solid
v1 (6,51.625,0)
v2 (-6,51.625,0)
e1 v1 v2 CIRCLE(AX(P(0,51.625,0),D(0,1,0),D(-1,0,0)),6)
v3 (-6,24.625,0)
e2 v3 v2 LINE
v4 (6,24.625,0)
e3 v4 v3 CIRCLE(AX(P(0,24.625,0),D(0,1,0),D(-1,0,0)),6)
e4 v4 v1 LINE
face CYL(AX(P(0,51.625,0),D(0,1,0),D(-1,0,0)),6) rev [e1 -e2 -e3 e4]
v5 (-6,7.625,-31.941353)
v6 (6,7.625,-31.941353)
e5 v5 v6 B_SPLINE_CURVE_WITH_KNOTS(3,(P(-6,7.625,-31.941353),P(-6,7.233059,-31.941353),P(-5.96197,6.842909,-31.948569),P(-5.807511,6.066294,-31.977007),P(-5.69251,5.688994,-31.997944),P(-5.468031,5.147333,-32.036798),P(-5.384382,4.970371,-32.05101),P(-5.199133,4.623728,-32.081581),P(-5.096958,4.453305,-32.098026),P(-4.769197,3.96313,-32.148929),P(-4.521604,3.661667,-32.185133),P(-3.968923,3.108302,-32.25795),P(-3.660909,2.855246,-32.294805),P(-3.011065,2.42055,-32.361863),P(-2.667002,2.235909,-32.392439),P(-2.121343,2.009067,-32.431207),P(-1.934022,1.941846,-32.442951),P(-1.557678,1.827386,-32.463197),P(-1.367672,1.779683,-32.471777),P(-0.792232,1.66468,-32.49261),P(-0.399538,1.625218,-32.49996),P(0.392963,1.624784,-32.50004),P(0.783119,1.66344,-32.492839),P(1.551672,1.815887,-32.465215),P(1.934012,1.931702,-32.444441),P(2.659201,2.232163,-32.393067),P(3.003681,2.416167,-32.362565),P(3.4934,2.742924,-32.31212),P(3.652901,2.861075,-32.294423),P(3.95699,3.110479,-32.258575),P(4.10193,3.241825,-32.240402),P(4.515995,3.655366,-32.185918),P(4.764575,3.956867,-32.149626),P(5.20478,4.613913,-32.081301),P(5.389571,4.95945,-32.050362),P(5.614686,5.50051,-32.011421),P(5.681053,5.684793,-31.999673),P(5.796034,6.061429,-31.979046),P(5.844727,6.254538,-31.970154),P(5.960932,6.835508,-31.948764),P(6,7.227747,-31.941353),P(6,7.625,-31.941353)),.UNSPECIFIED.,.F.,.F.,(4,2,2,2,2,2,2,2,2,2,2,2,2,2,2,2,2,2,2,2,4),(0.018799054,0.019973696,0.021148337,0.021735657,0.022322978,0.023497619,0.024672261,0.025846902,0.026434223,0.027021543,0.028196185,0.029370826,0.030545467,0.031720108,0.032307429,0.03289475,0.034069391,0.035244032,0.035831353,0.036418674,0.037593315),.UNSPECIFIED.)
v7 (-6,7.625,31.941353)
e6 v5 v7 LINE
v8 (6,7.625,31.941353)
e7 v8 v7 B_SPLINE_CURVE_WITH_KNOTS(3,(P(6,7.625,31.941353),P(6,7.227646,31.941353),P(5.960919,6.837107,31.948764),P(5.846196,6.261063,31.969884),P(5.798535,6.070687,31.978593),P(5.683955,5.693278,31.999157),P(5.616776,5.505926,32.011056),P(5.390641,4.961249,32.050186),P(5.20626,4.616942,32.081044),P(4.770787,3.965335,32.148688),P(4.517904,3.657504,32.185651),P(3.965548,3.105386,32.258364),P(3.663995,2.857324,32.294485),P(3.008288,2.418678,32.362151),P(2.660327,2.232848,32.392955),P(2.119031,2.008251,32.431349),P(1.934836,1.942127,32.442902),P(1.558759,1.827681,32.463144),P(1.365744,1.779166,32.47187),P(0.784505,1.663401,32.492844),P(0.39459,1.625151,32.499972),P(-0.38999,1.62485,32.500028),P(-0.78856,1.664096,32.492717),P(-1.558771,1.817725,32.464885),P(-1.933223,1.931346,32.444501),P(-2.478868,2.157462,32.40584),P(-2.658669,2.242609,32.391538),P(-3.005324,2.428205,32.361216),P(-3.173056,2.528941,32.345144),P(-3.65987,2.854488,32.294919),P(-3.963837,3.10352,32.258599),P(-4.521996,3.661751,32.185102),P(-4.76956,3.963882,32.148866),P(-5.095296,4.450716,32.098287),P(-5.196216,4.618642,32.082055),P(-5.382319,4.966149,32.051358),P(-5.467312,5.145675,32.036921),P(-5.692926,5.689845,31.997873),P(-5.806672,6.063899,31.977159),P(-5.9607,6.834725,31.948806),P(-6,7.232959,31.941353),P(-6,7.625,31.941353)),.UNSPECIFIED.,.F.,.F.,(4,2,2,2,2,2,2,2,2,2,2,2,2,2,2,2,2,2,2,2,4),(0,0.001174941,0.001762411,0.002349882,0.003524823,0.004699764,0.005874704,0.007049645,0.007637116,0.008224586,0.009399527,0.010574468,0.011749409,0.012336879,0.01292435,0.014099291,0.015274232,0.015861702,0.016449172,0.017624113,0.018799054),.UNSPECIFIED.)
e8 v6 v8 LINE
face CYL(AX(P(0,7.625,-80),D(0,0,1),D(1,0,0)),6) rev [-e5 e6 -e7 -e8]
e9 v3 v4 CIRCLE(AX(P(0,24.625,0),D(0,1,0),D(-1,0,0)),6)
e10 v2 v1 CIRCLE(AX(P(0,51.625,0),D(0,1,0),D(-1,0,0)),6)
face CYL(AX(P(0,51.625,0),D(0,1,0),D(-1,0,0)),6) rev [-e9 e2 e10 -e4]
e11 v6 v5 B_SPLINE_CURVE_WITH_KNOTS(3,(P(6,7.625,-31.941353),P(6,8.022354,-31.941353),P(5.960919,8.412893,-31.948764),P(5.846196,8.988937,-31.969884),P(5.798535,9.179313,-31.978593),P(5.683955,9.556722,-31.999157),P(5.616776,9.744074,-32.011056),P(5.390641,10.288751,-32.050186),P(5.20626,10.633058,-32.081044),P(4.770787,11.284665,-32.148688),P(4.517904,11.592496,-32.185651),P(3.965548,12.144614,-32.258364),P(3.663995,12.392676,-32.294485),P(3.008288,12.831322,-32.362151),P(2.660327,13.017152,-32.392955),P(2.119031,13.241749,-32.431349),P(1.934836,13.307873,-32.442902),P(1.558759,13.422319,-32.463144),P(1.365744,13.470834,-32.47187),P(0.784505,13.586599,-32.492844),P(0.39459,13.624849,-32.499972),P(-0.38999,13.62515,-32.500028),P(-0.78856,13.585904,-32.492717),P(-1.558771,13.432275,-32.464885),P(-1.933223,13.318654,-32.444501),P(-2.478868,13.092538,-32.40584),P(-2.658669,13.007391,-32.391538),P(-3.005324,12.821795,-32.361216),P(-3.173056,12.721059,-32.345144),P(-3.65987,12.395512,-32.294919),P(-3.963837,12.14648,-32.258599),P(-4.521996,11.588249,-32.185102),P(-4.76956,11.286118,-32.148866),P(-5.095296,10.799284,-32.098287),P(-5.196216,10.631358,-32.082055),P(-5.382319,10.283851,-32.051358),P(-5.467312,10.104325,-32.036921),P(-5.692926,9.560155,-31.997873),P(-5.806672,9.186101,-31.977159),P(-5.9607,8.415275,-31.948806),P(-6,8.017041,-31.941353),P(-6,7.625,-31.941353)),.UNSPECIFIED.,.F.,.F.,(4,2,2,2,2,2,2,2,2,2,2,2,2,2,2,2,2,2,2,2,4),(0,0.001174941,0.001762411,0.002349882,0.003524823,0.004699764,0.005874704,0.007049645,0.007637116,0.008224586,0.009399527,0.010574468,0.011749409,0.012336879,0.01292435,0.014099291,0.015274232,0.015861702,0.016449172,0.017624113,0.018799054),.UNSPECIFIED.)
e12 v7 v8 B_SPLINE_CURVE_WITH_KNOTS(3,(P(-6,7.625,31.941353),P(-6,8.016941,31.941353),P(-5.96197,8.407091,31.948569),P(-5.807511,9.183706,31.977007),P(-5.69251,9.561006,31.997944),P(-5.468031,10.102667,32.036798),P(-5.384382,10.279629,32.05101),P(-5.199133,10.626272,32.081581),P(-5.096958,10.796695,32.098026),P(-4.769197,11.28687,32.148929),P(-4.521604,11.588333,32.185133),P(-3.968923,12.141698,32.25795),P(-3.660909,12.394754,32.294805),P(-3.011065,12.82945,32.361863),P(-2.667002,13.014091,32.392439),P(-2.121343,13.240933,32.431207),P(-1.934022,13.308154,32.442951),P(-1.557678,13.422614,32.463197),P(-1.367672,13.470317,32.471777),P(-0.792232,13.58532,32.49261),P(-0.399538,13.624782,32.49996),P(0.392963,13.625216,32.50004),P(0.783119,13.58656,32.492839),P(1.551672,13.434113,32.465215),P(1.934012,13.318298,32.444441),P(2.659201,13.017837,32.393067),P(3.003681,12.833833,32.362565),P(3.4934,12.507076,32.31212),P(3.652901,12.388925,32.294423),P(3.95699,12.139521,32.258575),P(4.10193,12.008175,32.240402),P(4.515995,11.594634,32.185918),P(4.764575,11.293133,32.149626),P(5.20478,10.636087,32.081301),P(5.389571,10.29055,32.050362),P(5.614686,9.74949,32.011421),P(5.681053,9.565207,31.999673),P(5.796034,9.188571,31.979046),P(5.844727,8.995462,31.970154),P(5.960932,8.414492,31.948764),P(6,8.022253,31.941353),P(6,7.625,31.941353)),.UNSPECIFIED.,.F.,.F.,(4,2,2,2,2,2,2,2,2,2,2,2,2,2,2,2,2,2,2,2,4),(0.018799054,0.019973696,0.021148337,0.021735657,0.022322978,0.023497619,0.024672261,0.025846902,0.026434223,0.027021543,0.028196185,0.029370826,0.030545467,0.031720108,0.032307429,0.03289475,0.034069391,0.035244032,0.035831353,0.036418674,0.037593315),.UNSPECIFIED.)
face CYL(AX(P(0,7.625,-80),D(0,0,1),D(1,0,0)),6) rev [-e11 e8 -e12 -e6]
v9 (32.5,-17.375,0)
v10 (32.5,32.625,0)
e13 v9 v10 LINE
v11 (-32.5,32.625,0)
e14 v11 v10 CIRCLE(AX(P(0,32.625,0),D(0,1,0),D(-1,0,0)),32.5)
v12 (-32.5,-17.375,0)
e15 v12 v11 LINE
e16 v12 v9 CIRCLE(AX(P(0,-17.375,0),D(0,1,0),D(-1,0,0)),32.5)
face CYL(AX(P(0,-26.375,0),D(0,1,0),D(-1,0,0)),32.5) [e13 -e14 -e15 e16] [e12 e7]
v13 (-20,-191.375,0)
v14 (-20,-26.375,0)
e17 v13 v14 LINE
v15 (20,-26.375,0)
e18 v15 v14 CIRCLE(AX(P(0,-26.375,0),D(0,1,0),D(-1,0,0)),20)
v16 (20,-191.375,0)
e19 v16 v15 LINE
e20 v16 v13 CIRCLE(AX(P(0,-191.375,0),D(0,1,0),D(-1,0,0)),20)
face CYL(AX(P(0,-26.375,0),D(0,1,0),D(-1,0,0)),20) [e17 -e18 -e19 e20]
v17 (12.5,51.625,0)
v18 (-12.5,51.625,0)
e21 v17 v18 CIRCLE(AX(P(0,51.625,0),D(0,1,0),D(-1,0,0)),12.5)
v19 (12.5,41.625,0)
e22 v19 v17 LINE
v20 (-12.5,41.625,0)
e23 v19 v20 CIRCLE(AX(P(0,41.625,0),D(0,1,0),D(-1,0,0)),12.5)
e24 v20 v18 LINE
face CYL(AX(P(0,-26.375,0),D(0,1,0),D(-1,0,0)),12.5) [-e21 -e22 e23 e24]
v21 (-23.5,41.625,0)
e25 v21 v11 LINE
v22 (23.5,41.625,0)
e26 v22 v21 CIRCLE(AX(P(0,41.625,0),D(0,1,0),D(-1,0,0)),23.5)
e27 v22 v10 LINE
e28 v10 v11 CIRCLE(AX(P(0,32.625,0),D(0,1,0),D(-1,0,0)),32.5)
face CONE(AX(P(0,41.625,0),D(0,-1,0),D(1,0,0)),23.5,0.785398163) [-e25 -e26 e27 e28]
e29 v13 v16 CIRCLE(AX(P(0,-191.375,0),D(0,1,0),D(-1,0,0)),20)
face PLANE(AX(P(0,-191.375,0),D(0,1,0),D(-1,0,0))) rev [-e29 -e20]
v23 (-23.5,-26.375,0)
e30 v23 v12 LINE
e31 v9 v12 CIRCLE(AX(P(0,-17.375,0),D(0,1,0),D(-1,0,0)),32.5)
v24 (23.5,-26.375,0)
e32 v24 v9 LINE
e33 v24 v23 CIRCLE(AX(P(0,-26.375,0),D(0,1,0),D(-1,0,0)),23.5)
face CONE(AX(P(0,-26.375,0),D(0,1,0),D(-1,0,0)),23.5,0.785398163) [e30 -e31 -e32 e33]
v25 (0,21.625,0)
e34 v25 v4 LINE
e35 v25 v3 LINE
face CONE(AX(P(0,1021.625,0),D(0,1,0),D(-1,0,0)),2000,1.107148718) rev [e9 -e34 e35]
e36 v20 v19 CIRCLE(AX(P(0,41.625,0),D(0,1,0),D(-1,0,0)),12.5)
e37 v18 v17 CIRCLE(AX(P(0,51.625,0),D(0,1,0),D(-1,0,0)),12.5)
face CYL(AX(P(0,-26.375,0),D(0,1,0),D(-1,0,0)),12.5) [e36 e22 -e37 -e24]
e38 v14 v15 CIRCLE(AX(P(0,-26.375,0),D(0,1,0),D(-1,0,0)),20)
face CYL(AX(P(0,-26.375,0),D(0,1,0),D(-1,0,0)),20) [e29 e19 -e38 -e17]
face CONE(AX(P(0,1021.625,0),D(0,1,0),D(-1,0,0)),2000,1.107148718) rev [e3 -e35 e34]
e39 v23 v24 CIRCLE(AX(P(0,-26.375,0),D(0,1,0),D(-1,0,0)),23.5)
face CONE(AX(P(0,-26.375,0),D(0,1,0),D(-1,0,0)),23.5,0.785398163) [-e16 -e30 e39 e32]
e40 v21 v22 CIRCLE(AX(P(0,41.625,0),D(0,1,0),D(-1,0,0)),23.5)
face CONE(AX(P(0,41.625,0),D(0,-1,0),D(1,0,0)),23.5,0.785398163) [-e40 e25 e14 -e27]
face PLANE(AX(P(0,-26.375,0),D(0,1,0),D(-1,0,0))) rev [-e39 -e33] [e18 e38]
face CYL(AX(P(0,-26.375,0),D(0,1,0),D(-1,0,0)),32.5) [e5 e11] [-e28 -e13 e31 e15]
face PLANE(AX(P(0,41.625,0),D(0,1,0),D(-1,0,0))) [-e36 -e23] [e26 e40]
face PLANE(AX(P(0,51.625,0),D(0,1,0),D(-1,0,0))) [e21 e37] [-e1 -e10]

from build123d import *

# Parameters (mm, degrees)
SKETCH1_W          = 20
SKETCH1_H          = 165
SKETCH1_W_2        = 32.5
SKETCH1_H_2        = 50
SKETCH1_W_3        = 12.5
SKETCH1_H_3        = 10
SKETCH6_R          = 6
CUT_EXTRUDE1_DEPTH = 80


with BuildPart() as part:
    # Sketch1 → Revolve7 (revolve)
    with BuildSketch(Plane.XY, mode=Mode.PRIVATE) as revolve7_sk:
        with Locations((10, -108.875)):
            Rectangle(SKETCH1_W, SKETCH1_H)
        Polygon((0, -26.375), (23.5, -26.375), (32.5, -17.375), (0, -17.375), align=None)
        with Locations((16.25, 7.625)):
            Rectangle(SKETCH1_W_2, SKETCH1_H_2)
        Polygon((0, 32.625), (0, 41.625), (23.5, 41.625), (32.5, 32.625), align=None)
        with Locations((6.25, 46.625)):
            Rectangle(SKETCH1_W_3, SKETCH1_H_3)
    revolve(revolve7_sk.sketch.rotate(Axis((0, -26.375, 0), (0, -1, 0)), 180), axis=Axis((0, -26.375, 0), (0, -1, 0)))

    # Sketch5 → Cut-Revolve1 (revolve, cut)
    with BuildSketch(Plane.XY, mode=Mode.PRIVATE) as cut_revolve1_sk:
        Polygon((0, 51.625), (0, 24.625), (0, 21.625), (6, 24.625), (6, 51.625), align=None)
    revolve(cut_revolve1_sk.sketch.rotate(Axis((0, 51.625, 0), (0, -1, 0)), 180), axis=Axis((0, 51.625, 0), (0, -1, 0)), mode=Mode.SUBTRACT)

    # Sketch6 → Cut-Extrude1 (cut, symmetric)
    with BuildSketch(Plane.XY):
        with Locations((0, 7.625)):
            Circle(SKETCH6_R)
    extrude(amount=CUT_EXTRUDE1_DEPTH, both=True, mode=Mode.SUBTRACT)


solid = part.part
